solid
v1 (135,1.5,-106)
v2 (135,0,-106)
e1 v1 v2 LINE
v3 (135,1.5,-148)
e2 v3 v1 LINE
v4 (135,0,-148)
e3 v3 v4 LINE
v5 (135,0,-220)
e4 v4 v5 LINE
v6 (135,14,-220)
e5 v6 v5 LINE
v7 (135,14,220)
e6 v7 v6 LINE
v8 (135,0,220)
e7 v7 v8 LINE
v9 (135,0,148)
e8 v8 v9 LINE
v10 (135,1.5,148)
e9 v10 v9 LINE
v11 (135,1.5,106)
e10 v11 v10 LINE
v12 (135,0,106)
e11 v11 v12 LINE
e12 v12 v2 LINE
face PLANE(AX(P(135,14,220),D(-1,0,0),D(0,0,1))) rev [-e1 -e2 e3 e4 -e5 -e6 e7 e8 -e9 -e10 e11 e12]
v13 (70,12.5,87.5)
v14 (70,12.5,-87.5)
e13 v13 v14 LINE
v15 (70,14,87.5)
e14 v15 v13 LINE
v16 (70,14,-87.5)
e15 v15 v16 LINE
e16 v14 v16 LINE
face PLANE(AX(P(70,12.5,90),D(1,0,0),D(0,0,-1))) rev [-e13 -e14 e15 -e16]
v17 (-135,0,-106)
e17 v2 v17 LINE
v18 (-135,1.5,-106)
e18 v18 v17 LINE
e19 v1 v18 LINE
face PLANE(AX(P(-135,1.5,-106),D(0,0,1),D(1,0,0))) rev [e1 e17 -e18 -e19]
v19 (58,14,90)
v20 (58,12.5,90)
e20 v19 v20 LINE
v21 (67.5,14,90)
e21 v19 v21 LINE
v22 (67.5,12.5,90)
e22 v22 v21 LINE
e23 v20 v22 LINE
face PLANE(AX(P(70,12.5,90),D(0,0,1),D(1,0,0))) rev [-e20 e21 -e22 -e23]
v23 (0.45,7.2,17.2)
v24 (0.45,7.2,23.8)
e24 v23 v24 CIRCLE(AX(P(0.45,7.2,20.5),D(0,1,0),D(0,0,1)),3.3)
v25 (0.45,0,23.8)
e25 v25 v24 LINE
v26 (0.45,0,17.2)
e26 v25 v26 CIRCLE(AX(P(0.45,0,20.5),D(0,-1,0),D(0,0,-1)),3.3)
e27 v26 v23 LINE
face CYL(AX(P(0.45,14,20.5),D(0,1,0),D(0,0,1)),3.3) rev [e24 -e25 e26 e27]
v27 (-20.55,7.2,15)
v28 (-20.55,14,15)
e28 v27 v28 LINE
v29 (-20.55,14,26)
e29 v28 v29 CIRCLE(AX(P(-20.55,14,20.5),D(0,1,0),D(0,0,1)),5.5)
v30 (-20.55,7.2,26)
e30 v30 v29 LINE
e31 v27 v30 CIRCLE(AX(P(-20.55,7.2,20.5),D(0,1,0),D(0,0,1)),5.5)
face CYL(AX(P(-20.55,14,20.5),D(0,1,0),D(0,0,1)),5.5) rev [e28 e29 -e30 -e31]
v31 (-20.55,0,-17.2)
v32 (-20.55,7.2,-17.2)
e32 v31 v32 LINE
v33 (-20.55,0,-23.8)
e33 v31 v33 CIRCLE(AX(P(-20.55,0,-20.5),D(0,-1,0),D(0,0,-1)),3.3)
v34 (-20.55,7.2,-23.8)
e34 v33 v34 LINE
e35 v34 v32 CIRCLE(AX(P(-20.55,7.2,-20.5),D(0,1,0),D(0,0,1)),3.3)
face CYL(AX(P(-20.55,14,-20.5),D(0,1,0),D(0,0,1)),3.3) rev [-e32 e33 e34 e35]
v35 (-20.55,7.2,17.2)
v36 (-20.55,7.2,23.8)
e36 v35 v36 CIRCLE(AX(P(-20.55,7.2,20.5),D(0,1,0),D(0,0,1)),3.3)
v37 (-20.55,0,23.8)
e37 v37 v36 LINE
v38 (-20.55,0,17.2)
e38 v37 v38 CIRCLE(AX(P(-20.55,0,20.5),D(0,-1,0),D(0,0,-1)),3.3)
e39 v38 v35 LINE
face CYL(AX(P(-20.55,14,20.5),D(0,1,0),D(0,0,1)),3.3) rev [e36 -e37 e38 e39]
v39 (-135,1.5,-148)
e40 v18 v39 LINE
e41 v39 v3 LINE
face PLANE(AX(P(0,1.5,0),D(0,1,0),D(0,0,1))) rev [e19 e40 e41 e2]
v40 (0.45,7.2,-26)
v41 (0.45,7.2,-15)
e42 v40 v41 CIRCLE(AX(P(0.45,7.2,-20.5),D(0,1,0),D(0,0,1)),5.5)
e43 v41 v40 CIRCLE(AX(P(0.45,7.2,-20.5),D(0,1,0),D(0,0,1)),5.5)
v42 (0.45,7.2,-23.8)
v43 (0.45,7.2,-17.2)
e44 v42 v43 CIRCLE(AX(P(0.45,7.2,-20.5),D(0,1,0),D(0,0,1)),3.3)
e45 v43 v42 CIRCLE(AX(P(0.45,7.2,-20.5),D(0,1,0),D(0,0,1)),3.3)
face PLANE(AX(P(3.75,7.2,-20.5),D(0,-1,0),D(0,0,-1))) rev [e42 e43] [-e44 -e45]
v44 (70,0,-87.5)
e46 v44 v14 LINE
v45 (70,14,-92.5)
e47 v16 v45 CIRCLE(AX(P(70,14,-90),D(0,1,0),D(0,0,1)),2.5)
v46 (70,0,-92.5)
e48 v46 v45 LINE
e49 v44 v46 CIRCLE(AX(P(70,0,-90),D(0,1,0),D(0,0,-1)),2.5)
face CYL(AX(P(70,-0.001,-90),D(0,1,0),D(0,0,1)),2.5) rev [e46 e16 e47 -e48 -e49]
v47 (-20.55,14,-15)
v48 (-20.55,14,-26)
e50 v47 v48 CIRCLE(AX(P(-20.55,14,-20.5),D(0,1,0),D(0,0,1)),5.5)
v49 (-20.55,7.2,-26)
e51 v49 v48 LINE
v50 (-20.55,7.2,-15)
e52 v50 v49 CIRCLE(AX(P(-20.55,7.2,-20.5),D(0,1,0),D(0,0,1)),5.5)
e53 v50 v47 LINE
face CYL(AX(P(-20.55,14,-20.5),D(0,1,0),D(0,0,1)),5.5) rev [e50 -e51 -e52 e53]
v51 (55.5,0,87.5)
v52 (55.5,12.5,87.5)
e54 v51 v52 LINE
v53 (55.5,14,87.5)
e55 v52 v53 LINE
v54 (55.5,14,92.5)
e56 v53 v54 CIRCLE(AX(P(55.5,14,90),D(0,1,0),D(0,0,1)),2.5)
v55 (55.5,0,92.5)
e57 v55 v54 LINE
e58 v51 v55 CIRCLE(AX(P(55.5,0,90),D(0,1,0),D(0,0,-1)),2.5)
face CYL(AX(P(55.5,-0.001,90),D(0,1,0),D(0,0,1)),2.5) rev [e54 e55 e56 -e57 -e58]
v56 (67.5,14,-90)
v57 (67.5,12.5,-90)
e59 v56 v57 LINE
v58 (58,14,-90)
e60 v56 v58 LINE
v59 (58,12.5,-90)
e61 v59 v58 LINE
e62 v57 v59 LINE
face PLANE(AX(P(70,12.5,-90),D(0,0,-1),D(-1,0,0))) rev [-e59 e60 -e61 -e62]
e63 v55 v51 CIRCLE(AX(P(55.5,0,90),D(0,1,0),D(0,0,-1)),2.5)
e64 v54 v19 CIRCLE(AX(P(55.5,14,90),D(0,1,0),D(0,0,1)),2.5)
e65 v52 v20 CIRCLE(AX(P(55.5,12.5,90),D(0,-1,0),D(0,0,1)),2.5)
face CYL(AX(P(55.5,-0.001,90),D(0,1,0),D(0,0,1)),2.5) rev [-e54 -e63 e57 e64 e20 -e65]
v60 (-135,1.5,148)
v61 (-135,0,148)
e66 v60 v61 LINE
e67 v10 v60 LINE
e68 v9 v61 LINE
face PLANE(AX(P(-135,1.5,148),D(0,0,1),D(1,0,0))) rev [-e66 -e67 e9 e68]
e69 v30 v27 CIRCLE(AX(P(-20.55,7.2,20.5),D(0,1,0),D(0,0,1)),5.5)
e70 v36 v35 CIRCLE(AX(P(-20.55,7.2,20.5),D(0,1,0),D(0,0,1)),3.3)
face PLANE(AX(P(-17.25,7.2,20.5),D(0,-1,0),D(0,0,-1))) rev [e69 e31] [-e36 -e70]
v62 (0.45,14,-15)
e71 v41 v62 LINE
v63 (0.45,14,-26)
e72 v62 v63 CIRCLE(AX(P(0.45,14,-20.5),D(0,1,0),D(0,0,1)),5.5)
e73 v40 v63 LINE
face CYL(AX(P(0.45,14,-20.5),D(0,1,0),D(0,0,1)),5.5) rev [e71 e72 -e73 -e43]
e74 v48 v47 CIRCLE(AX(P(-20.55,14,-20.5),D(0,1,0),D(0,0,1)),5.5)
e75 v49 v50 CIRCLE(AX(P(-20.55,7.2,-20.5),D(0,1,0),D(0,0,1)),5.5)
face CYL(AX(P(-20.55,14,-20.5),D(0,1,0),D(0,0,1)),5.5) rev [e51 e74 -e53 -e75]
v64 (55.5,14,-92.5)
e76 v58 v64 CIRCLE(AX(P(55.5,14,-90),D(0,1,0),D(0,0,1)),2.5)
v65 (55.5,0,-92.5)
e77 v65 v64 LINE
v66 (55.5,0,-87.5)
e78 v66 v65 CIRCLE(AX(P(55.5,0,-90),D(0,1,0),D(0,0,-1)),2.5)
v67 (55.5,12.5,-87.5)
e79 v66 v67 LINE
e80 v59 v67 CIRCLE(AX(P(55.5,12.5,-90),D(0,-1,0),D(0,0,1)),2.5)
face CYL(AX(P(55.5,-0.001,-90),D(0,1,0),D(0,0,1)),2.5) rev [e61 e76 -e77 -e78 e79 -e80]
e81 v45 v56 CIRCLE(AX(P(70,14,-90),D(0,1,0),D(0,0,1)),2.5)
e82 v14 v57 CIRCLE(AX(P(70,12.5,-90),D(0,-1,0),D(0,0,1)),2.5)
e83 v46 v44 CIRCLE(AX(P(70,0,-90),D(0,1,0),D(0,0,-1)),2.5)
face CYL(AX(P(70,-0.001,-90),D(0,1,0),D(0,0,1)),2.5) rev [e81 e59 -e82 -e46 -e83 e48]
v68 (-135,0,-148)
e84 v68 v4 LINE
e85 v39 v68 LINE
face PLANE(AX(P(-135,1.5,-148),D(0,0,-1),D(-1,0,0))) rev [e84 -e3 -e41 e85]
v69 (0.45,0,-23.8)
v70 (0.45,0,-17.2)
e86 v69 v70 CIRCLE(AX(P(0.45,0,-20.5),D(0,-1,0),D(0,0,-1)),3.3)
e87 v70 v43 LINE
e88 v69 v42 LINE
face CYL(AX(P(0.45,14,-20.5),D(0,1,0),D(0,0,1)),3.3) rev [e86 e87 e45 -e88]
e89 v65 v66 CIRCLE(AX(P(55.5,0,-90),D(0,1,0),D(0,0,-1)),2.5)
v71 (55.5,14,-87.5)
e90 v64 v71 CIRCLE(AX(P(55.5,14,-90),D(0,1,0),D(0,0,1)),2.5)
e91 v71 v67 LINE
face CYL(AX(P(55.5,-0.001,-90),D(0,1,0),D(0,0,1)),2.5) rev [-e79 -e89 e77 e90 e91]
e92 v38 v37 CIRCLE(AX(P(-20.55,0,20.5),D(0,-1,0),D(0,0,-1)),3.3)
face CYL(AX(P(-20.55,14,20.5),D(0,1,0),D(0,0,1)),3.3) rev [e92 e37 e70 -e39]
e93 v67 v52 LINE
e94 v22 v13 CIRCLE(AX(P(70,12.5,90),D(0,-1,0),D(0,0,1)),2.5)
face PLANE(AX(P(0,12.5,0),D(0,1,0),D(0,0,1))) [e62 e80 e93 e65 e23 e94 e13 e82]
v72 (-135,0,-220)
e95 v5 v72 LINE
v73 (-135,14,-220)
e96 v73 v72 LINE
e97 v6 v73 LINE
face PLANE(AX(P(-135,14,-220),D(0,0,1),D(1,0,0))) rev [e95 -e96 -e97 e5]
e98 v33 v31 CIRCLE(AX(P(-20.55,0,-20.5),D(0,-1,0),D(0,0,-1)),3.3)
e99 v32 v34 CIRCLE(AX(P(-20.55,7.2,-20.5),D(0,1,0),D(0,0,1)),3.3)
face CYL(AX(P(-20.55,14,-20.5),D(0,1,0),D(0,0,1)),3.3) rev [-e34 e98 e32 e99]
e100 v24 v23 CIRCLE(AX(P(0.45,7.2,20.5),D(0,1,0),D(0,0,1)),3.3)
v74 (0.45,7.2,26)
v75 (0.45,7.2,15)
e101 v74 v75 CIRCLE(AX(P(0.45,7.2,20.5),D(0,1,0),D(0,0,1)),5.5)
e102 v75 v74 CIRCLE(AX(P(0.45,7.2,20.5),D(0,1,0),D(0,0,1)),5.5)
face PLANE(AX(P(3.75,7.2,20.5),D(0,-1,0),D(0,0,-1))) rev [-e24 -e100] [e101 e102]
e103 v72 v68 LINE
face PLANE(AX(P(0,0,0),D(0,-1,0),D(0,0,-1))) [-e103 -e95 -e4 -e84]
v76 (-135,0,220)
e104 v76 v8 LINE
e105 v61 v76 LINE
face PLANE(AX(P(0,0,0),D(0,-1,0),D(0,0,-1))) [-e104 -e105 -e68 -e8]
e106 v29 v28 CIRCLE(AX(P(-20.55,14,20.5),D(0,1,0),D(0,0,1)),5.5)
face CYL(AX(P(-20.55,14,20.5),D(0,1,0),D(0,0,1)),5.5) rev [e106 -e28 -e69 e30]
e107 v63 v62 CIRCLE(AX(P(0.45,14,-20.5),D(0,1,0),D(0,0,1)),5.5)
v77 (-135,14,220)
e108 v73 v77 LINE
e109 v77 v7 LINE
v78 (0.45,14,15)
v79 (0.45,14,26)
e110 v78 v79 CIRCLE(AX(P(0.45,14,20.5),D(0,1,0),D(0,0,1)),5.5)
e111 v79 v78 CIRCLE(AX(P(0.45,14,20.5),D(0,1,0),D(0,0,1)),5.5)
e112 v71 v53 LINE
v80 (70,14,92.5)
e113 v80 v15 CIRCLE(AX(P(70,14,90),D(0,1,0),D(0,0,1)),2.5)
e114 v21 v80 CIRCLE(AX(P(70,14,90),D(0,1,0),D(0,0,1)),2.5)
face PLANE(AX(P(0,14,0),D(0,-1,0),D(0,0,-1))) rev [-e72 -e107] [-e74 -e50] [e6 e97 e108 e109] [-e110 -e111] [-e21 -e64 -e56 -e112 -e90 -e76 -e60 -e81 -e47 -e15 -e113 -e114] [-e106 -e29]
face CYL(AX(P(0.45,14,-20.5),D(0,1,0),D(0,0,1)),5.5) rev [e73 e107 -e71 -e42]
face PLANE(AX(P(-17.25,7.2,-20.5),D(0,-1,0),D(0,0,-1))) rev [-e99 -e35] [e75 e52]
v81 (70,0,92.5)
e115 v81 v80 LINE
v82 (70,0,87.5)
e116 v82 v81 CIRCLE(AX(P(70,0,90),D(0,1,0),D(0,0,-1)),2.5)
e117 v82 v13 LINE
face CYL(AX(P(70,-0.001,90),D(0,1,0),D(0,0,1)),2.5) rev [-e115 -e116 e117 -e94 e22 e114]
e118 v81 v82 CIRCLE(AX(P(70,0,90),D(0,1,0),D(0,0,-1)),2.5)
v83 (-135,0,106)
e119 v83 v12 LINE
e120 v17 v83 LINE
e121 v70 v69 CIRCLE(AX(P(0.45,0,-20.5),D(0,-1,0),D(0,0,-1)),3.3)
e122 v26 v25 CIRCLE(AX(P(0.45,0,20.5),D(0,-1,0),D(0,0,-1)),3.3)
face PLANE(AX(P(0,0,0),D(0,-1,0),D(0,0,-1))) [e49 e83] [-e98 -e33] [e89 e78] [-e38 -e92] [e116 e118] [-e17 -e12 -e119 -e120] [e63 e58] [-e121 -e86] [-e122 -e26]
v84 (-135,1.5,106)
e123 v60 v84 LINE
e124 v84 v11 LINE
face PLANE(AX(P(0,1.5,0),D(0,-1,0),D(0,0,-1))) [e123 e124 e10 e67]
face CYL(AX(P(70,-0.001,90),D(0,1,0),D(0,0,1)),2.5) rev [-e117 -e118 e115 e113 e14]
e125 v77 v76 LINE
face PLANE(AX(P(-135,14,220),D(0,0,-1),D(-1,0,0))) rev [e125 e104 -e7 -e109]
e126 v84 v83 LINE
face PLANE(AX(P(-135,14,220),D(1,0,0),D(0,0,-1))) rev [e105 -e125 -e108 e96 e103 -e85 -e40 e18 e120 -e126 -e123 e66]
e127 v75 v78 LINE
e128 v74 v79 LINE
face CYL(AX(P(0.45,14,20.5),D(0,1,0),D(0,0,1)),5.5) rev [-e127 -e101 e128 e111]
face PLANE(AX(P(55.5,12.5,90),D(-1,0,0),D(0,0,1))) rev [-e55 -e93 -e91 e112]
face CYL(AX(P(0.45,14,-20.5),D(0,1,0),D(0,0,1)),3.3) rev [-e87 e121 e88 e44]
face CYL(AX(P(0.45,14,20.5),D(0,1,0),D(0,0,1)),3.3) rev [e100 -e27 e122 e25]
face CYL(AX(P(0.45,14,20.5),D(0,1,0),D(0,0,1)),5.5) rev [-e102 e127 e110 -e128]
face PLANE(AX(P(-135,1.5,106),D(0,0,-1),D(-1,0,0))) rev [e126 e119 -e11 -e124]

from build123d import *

# Parameters (mm, degrees)
SKETCH_1_W                = 270
SKETCH_1_H                = 440
EXTRUDE_1_DEPTH           = 14
SKETCH_2_W                = 270
SKETCH_2_H                = 42
CUT_EXTRUDE_1_DEPTH       = 1.5
HOLE_WIZARD_1_D           = 6.6
HOLE_WIZARD_1_CBORE_D     = 11
HOLE_WIZARD_1_CBORE_DEPTH = 6.8
SKETCH_4_W                = 14.5
SKETCH_4_H                = 180
CUT_EXTRUDE_2_DEPTH       = 1.5
CUT_EXTRUDE_3_REACH       = 260.498
SKETCH_5_R                = 2.5


with BuildPart() as part:
    # 草图1 → 凸台-拉伸1 (new body)
    with BuildSketch(Plane(origin=(0, 0, 0), x_dir=(1, 0, 0), z_dir=(0, 1, 0))):
        Rectangle(SKETCH_1_W, SKETCH_1_H)
    extrude(amount=EXTRUDE_1_DEPTH)

    # 草图2 → 切除-拉伸1 (cut)
    with BuildSketch(Plane.XZ):
        with Locations((0, 127)):
            Rectangle(SKETCH_2_W, SKETCH_2_H)
        with Locations((0, -127)):
            Rectangle(SKETCH_2_W, SKETCH_2_H)
    extrude(amount=-CUT_EXTRUDE_1_DEPTH, mode=Mode.SUBTRACT)

    # 打孔尺寸(%根据)内六角圆柱头螺钉的类型1 (through all)
    with Locations(Plane(origin=(-20.55, 14, 20.5), x_dir=(0, 0, 1), z_dir=(0, 1, 0))):
        with Locations((0, 0), (-41, 0), (0, 21), (-41, 21)):
            CounterBoreHole(HOLE_WIZARD_1_D / 2, HOLE_WIZARD_1_CBORE_D / 2, HOLE_WIZARD_1_CBORE_DEPTH)

    # 草图4 → 切除-拉伸2 (cut)
    with BuildSketch(Plane(origin=(0, 14, 0), x_dir=(1, 0, 0), z_dir=(0, 1, 0))):
        with Locations((62.75, 0)):
            Rectangle(SKETCH_4_W, SKETCH_4_H)
    extrude(amount=-CUT_EXTRUDE_2_DEPTH, mode=Mode.SUBTRACT)

    # 草图5 → 切除-拉伸3 (cut, up to next)
    with BuildSketch(Plane(origin=(0, 14, 0), x_dir=(1, 0, 0), z_dir=(0, 1, 0)), mode=Mode.PRIVATE) as cut_extrude_3_sk1:
        with Locations(Location((55.5, 90, 0), (0, 0, 270))):
            Circle(SKETCH_5_R)
    cut_extrude_3_tool1 = extrude(cut_extrude_3_sk1.sketch, amount=-CUT_EXTRUDE_3_REACH, mode=Mode.PRIVATE) & part.part
    # 草图5 → 切除-拉伸3 (cut, up to next)
    with BuildSketch(Plane(origin=(0, 14, 0), x_dir=(1, 0, 0), z_dir=(0, 1, 0)), mode=Mode.PRIVATE) as cut_extrude_3_sk2:
        with Locations(Location((70, 90, 0), (0, 0, 270))):
            Circle(SKETCH_5_R)
    cut_extrude_3_tool2 = extrude(cut_extrude_3_sk2.sketch, amount=-CUT_EXTRUDE_3_REACH, mode=Mode.PRIVATE) & part.part
    # 草图5 → 切除-拉伸3 (cut, up to next)
    with BuildSketch(Plane(origin=(0, 14, 0), x_dir=(1, 0, 0), z_dir=(0, 1, 0)), mode=Mode.PRIVATE) as cut_extrude_3_sk3:
        with Locations(Location((55.5, -90, 0), (0, 0, 90))):
            Circle(SKETCH_5_R)
    cut_extrude_3_tool3 = extrude(cut_extrude_3_sk3.sketch, amount=-CUT_EXTRUDE_3_REACH, mode=Mode.PRIVATE) & part.part
    # 草图5 → 切除-拉伸3 (cut, up to next)
    with BuildSketch(Plane(origin=(0, 14, 0), x_dir=(1, 0, 0), z_dir=(0, 1, 0)), mode=Mode.PRIVATE) as cut_extrude_3_sk4:
        with Locations(Location((70, -90, 0), (0, 0, 90))):
            Circle(SKETCH_5_R)
    cut_extrude_3_tool4 = extrude(cut_extrude_3_sk4.sketch, amount=-CUT_EXTRUDE_3_REACH, mode=Mode.PRIVATE) & part.part
    add(cut_extrude_3_tool1.solids().sort_by_distance((55.5, 14, -90))[0], mode=Mode.SUBTRACT)
    add(cut_extrude_3_tool2.solids().sort_by_distance((70, 14, -90))[0], mode=Mode.SUBTRACT)
    add(cut_extrude_3_tool3.solids().sort_by_distance((55.5, 14, 90))[0], mode=Mode.SUBTRACT)
    add(cut_extrude_3_tool4.solids().sort_by_distance((70, 14, 90))[0], mode=Mode.SUBTRACT)


solid = part.part
